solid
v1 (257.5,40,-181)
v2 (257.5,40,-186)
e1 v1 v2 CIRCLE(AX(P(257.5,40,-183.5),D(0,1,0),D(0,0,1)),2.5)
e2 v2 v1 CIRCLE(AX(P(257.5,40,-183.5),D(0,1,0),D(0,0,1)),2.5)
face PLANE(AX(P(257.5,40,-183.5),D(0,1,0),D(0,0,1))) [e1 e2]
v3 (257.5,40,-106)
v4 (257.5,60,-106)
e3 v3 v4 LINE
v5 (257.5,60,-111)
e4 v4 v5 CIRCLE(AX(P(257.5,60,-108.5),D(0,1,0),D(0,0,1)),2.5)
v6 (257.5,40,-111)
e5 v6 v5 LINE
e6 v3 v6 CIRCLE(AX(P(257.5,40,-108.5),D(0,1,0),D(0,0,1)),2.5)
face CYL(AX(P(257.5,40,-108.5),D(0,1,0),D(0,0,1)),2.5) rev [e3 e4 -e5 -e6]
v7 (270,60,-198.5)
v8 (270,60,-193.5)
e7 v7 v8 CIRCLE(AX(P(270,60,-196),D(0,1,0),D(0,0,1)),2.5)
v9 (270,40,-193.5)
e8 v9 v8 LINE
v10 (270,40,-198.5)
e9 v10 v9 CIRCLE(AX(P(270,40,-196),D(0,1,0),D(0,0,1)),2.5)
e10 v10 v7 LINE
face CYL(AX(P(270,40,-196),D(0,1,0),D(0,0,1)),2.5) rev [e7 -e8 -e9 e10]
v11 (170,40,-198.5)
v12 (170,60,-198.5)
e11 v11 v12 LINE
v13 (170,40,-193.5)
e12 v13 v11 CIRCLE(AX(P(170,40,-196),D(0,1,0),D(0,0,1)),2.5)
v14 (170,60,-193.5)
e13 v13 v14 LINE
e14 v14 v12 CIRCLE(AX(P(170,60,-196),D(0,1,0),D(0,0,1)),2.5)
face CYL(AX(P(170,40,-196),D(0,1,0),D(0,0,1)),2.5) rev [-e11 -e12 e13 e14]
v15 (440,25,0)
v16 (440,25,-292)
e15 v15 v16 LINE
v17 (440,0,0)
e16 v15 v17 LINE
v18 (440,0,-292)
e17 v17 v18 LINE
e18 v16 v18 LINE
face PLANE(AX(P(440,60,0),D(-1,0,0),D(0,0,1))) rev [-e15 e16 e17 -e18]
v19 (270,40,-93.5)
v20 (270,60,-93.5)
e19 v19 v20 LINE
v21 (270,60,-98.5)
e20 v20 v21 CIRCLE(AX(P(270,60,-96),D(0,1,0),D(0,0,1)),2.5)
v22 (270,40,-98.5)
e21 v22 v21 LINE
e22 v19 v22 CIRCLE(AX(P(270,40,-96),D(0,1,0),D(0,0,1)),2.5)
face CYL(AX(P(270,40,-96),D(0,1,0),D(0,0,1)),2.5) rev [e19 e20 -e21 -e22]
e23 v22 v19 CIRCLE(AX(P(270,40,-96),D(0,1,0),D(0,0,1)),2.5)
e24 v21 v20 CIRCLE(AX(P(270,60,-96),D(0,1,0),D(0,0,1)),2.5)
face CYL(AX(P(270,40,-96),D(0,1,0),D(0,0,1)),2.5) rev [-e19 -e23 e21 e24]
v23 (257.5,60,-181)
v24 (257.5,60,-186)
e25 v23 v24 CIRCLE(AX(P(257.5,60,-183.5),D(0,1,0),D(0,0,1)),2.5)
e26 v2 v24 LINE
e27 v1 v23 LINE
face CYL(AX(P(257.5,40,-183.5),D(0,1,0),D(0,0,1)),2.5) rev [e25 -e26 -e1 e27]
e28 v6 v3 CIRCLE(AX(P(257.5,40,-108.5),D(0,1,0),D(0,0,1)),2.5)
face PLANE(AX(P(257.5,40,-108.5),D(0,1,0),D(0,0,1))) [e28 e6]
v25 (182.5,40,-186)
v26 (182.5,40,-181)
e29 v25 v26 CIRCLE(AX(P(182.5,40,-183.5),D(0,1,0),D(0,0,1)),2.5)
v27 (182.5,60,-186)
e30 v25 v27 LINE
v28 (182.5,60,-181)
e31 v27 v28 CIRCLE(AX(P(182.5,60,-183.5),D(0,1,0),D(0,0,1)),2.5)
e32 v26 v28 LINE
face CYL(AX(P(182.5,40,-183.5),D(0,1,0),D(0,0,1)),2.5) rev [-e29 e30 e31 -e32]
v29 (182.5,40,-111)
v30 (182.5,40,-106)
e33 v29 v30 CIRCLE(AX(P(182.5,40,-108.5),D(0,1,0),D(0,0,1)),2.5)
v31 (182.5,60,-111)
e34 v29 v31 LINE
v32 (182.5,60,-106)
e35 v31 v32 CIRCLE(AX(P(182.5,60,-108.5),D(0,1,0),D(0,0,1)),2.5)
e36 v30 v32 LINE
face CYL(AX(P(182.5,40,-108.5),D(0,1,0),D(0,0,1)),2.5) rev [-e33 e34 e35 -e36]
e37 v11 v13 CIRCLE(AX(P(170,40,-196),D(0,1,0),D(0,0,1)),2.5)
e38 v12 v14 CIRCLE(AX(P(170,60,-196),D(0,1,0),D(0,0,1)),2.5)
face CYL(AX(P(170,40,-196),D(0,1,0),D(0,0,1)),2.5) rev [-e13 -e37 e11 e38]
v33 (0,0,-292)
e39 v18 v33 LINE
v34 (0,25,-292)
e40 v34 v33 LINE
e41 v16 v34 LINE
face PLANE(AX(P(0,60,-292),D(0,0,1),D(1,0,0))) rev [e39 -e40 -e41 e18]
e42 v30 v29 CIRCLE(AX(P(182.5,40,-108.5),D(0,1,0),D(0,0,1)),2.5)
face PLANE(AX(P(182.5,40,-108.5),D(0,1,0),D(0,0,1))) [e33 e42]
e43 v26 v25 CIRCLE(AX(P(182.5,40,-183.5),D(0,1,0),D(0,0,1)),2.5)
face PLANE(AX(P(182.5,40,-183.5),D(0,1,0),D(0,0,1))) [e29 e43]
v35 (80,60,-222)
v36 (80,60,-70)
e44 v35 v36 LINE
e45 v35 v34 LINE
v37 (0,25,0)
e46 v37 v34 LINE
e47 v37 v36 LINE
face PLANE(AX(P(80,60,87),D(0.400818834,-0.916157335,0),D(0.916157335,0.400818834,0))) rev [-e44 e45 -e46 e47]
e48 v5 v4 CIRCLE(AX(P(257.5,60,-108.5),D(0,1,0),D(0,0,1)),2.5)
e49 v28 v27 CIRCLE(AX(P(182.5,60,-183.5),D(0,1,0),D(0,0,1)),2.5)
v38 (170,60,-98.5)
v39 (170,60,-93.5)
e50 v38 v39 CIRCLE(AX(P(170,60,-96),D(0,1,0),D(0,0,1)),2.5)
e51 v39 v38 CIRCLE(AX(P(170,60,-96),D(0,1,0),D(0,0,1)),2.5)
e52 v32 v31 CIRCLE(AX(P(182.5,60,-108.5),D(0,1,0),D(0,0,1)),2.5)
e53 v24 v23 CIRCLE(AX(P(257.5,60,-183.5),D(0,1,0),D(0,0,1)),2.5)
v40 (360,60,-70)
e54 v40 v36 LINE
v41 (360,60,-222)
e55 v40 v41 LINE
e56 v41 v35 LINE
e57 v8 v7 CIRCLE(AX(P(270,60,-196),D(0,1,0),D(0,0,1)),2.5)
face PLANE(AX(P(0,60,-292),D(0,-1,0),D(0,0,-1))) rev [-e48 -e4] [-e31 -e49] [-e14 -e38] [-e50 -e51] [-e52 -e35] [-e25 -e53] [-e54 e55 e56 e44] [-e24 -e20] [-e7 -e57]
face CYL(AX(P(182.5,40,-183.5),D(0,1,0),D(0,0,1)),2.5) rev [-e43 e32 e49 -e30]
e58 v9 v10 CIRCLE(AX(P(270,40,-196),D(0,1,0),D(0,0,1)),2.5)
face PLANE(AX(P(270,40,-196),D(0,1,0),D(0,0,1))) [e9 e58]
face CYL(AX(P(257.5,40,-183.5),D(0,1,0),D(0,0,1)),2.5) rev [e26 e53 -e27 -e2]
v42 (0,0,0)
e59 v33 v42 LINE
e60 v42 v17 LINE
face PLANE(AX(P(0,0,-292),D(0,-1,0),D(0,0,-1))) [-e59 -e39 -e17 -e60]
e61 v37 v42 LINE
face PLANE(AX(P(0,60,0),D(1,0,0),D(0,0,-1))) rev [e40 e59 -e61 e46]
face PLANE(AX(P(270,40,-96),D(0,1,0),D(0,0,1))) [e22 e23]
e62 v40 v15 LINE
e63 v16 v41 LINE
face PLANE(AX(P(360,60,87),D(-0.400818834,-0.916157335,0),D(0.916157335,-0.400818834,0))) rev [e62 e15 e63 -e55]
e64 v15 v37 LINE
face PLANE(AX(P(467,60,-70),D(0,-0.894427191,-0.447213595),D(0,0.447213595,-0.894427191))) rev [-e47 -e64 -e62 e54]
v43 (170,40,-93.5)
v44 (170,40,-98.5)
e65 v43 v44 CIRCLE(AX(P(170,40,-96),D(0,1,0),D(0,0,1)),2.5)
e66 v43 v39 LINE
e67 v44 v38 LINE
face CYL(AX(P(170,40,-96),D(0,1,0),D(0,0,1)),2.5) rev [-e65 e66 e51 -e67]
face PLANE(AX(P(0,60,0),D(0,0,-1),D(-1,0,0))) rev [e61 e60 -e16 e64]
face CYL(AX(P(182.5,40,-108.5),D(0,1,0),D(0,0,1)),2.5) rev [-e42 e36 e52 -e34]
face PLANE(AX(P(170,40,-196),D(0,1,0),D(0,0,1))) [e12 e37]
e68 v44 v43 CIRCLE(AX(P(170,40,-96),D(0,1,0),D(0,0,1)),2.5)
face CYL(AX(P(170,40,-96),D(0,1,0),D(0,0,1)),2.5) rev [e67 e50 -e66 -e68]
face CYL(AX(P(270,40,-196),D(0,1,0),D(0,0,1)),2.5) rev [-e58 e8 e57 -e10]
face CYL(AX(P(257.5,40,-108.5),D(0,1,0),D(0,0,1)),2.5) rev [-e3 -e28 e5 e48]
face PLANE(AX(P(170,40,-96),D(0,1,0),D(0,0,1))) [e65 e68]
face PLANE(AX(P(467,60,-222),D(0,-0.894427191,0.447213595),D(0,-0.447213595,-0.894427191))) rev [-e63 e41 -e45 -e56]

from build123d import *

# Parameters (mm, degrees)
SKETCH_1_W          = 440
SKETCH_1_H          = 292
EXTRUDE_1_DEPTH     = 60
CUT_EXTRUDE_1_DEPTH = 379
CUT_EXTRUDE_2_DEPTH = 467
SKETCH_5_R          = 2.5
CUT_EXTRUDE_3_DEPTH = 20


with BuildPart() as part:
    # 草图1 → 凸台-拉伸1 (new body)
    with BuildSketch(Plane(origin=(0, 0, 0), x_dir=(1, 0, 0), z_dir=(0, 1, 0))):
        with Locations((220, 146)):
            Rectangle(SKETCH_1_W, SKETCH_1_H)
    extrude(amount=EXTRUDE_1_DEPTH)

    # 草图3 → 切除-拉伸1 (cut)
    with BuildSketch(Plane(origin=(0, 0, -292), x_dir=(-1, 0, 0), z_dir=(0, 0, -1))):
        Polygon((-440, 60), (-440, 25), (-360, 60), align=None)
        Polygon((-80, 60), (0, 25), (0, 60), align=None)
    extrude(amount=-CUT_EXTRUDE_1_DEPTH, mode=Mode.SUBTRACT)

    # 草图4 → 切除-拉伸2 (cut)
    with BuildSketch(Plane.ZY):
        Polygon((-292, 60), (-292, 25), (-222, 60), align=None)
        Polygon((-70, 60), (0, 25), (0, 60), align=None)
    extrude(amount=-CUT_EXTRUDE_2_DEPTH, mode=Mode.SUBTRACT)

    # 草图5 → 切除-拉伸3 (cut)
    with BuildSketch(Plane(origin=(0, 60, 0), x_dir=(1, 0, 0), z_dir=(0, 1, 0))):
        with Locations(Location((270, 196, 0), (0, 0, 270))):
            Circle(SKETCH_5_R)
        with Locations(Location((257.5, 183.5, 0), (0, 0, 270))):
            Circle(SKETCH_5_R)
        with Locations(Location((270, 96, 0), (0, 0, 270))):
            Circle(SKETCH_5_R)
        with Locations(Location((257.5, 108.5, 0), (0, 0, 270))):
            Circle(SKETCH_5_R)
        with Locations(Location((170, 96, 0), (0, 0, 270))):
            Circle(SKETCH_5_R)
        with Locations(Location((182.5, 108.5, 0), (0, 0, 270))):
            Circle(SKETCH_5_R)
        with Locations(Location((170, 196, 0), (0, 0, 270))):
            Circle(SKETCH_5_R)
        with Locations(Location((182.5, 183.5, 0), (0, 0, 270))):
            Circle(SKETCH_5_R)
    extrude(amount=-CUT_EXTRUDE_3_DEPTH, mode=Mode.SUBTRACT)


solid = part.part
